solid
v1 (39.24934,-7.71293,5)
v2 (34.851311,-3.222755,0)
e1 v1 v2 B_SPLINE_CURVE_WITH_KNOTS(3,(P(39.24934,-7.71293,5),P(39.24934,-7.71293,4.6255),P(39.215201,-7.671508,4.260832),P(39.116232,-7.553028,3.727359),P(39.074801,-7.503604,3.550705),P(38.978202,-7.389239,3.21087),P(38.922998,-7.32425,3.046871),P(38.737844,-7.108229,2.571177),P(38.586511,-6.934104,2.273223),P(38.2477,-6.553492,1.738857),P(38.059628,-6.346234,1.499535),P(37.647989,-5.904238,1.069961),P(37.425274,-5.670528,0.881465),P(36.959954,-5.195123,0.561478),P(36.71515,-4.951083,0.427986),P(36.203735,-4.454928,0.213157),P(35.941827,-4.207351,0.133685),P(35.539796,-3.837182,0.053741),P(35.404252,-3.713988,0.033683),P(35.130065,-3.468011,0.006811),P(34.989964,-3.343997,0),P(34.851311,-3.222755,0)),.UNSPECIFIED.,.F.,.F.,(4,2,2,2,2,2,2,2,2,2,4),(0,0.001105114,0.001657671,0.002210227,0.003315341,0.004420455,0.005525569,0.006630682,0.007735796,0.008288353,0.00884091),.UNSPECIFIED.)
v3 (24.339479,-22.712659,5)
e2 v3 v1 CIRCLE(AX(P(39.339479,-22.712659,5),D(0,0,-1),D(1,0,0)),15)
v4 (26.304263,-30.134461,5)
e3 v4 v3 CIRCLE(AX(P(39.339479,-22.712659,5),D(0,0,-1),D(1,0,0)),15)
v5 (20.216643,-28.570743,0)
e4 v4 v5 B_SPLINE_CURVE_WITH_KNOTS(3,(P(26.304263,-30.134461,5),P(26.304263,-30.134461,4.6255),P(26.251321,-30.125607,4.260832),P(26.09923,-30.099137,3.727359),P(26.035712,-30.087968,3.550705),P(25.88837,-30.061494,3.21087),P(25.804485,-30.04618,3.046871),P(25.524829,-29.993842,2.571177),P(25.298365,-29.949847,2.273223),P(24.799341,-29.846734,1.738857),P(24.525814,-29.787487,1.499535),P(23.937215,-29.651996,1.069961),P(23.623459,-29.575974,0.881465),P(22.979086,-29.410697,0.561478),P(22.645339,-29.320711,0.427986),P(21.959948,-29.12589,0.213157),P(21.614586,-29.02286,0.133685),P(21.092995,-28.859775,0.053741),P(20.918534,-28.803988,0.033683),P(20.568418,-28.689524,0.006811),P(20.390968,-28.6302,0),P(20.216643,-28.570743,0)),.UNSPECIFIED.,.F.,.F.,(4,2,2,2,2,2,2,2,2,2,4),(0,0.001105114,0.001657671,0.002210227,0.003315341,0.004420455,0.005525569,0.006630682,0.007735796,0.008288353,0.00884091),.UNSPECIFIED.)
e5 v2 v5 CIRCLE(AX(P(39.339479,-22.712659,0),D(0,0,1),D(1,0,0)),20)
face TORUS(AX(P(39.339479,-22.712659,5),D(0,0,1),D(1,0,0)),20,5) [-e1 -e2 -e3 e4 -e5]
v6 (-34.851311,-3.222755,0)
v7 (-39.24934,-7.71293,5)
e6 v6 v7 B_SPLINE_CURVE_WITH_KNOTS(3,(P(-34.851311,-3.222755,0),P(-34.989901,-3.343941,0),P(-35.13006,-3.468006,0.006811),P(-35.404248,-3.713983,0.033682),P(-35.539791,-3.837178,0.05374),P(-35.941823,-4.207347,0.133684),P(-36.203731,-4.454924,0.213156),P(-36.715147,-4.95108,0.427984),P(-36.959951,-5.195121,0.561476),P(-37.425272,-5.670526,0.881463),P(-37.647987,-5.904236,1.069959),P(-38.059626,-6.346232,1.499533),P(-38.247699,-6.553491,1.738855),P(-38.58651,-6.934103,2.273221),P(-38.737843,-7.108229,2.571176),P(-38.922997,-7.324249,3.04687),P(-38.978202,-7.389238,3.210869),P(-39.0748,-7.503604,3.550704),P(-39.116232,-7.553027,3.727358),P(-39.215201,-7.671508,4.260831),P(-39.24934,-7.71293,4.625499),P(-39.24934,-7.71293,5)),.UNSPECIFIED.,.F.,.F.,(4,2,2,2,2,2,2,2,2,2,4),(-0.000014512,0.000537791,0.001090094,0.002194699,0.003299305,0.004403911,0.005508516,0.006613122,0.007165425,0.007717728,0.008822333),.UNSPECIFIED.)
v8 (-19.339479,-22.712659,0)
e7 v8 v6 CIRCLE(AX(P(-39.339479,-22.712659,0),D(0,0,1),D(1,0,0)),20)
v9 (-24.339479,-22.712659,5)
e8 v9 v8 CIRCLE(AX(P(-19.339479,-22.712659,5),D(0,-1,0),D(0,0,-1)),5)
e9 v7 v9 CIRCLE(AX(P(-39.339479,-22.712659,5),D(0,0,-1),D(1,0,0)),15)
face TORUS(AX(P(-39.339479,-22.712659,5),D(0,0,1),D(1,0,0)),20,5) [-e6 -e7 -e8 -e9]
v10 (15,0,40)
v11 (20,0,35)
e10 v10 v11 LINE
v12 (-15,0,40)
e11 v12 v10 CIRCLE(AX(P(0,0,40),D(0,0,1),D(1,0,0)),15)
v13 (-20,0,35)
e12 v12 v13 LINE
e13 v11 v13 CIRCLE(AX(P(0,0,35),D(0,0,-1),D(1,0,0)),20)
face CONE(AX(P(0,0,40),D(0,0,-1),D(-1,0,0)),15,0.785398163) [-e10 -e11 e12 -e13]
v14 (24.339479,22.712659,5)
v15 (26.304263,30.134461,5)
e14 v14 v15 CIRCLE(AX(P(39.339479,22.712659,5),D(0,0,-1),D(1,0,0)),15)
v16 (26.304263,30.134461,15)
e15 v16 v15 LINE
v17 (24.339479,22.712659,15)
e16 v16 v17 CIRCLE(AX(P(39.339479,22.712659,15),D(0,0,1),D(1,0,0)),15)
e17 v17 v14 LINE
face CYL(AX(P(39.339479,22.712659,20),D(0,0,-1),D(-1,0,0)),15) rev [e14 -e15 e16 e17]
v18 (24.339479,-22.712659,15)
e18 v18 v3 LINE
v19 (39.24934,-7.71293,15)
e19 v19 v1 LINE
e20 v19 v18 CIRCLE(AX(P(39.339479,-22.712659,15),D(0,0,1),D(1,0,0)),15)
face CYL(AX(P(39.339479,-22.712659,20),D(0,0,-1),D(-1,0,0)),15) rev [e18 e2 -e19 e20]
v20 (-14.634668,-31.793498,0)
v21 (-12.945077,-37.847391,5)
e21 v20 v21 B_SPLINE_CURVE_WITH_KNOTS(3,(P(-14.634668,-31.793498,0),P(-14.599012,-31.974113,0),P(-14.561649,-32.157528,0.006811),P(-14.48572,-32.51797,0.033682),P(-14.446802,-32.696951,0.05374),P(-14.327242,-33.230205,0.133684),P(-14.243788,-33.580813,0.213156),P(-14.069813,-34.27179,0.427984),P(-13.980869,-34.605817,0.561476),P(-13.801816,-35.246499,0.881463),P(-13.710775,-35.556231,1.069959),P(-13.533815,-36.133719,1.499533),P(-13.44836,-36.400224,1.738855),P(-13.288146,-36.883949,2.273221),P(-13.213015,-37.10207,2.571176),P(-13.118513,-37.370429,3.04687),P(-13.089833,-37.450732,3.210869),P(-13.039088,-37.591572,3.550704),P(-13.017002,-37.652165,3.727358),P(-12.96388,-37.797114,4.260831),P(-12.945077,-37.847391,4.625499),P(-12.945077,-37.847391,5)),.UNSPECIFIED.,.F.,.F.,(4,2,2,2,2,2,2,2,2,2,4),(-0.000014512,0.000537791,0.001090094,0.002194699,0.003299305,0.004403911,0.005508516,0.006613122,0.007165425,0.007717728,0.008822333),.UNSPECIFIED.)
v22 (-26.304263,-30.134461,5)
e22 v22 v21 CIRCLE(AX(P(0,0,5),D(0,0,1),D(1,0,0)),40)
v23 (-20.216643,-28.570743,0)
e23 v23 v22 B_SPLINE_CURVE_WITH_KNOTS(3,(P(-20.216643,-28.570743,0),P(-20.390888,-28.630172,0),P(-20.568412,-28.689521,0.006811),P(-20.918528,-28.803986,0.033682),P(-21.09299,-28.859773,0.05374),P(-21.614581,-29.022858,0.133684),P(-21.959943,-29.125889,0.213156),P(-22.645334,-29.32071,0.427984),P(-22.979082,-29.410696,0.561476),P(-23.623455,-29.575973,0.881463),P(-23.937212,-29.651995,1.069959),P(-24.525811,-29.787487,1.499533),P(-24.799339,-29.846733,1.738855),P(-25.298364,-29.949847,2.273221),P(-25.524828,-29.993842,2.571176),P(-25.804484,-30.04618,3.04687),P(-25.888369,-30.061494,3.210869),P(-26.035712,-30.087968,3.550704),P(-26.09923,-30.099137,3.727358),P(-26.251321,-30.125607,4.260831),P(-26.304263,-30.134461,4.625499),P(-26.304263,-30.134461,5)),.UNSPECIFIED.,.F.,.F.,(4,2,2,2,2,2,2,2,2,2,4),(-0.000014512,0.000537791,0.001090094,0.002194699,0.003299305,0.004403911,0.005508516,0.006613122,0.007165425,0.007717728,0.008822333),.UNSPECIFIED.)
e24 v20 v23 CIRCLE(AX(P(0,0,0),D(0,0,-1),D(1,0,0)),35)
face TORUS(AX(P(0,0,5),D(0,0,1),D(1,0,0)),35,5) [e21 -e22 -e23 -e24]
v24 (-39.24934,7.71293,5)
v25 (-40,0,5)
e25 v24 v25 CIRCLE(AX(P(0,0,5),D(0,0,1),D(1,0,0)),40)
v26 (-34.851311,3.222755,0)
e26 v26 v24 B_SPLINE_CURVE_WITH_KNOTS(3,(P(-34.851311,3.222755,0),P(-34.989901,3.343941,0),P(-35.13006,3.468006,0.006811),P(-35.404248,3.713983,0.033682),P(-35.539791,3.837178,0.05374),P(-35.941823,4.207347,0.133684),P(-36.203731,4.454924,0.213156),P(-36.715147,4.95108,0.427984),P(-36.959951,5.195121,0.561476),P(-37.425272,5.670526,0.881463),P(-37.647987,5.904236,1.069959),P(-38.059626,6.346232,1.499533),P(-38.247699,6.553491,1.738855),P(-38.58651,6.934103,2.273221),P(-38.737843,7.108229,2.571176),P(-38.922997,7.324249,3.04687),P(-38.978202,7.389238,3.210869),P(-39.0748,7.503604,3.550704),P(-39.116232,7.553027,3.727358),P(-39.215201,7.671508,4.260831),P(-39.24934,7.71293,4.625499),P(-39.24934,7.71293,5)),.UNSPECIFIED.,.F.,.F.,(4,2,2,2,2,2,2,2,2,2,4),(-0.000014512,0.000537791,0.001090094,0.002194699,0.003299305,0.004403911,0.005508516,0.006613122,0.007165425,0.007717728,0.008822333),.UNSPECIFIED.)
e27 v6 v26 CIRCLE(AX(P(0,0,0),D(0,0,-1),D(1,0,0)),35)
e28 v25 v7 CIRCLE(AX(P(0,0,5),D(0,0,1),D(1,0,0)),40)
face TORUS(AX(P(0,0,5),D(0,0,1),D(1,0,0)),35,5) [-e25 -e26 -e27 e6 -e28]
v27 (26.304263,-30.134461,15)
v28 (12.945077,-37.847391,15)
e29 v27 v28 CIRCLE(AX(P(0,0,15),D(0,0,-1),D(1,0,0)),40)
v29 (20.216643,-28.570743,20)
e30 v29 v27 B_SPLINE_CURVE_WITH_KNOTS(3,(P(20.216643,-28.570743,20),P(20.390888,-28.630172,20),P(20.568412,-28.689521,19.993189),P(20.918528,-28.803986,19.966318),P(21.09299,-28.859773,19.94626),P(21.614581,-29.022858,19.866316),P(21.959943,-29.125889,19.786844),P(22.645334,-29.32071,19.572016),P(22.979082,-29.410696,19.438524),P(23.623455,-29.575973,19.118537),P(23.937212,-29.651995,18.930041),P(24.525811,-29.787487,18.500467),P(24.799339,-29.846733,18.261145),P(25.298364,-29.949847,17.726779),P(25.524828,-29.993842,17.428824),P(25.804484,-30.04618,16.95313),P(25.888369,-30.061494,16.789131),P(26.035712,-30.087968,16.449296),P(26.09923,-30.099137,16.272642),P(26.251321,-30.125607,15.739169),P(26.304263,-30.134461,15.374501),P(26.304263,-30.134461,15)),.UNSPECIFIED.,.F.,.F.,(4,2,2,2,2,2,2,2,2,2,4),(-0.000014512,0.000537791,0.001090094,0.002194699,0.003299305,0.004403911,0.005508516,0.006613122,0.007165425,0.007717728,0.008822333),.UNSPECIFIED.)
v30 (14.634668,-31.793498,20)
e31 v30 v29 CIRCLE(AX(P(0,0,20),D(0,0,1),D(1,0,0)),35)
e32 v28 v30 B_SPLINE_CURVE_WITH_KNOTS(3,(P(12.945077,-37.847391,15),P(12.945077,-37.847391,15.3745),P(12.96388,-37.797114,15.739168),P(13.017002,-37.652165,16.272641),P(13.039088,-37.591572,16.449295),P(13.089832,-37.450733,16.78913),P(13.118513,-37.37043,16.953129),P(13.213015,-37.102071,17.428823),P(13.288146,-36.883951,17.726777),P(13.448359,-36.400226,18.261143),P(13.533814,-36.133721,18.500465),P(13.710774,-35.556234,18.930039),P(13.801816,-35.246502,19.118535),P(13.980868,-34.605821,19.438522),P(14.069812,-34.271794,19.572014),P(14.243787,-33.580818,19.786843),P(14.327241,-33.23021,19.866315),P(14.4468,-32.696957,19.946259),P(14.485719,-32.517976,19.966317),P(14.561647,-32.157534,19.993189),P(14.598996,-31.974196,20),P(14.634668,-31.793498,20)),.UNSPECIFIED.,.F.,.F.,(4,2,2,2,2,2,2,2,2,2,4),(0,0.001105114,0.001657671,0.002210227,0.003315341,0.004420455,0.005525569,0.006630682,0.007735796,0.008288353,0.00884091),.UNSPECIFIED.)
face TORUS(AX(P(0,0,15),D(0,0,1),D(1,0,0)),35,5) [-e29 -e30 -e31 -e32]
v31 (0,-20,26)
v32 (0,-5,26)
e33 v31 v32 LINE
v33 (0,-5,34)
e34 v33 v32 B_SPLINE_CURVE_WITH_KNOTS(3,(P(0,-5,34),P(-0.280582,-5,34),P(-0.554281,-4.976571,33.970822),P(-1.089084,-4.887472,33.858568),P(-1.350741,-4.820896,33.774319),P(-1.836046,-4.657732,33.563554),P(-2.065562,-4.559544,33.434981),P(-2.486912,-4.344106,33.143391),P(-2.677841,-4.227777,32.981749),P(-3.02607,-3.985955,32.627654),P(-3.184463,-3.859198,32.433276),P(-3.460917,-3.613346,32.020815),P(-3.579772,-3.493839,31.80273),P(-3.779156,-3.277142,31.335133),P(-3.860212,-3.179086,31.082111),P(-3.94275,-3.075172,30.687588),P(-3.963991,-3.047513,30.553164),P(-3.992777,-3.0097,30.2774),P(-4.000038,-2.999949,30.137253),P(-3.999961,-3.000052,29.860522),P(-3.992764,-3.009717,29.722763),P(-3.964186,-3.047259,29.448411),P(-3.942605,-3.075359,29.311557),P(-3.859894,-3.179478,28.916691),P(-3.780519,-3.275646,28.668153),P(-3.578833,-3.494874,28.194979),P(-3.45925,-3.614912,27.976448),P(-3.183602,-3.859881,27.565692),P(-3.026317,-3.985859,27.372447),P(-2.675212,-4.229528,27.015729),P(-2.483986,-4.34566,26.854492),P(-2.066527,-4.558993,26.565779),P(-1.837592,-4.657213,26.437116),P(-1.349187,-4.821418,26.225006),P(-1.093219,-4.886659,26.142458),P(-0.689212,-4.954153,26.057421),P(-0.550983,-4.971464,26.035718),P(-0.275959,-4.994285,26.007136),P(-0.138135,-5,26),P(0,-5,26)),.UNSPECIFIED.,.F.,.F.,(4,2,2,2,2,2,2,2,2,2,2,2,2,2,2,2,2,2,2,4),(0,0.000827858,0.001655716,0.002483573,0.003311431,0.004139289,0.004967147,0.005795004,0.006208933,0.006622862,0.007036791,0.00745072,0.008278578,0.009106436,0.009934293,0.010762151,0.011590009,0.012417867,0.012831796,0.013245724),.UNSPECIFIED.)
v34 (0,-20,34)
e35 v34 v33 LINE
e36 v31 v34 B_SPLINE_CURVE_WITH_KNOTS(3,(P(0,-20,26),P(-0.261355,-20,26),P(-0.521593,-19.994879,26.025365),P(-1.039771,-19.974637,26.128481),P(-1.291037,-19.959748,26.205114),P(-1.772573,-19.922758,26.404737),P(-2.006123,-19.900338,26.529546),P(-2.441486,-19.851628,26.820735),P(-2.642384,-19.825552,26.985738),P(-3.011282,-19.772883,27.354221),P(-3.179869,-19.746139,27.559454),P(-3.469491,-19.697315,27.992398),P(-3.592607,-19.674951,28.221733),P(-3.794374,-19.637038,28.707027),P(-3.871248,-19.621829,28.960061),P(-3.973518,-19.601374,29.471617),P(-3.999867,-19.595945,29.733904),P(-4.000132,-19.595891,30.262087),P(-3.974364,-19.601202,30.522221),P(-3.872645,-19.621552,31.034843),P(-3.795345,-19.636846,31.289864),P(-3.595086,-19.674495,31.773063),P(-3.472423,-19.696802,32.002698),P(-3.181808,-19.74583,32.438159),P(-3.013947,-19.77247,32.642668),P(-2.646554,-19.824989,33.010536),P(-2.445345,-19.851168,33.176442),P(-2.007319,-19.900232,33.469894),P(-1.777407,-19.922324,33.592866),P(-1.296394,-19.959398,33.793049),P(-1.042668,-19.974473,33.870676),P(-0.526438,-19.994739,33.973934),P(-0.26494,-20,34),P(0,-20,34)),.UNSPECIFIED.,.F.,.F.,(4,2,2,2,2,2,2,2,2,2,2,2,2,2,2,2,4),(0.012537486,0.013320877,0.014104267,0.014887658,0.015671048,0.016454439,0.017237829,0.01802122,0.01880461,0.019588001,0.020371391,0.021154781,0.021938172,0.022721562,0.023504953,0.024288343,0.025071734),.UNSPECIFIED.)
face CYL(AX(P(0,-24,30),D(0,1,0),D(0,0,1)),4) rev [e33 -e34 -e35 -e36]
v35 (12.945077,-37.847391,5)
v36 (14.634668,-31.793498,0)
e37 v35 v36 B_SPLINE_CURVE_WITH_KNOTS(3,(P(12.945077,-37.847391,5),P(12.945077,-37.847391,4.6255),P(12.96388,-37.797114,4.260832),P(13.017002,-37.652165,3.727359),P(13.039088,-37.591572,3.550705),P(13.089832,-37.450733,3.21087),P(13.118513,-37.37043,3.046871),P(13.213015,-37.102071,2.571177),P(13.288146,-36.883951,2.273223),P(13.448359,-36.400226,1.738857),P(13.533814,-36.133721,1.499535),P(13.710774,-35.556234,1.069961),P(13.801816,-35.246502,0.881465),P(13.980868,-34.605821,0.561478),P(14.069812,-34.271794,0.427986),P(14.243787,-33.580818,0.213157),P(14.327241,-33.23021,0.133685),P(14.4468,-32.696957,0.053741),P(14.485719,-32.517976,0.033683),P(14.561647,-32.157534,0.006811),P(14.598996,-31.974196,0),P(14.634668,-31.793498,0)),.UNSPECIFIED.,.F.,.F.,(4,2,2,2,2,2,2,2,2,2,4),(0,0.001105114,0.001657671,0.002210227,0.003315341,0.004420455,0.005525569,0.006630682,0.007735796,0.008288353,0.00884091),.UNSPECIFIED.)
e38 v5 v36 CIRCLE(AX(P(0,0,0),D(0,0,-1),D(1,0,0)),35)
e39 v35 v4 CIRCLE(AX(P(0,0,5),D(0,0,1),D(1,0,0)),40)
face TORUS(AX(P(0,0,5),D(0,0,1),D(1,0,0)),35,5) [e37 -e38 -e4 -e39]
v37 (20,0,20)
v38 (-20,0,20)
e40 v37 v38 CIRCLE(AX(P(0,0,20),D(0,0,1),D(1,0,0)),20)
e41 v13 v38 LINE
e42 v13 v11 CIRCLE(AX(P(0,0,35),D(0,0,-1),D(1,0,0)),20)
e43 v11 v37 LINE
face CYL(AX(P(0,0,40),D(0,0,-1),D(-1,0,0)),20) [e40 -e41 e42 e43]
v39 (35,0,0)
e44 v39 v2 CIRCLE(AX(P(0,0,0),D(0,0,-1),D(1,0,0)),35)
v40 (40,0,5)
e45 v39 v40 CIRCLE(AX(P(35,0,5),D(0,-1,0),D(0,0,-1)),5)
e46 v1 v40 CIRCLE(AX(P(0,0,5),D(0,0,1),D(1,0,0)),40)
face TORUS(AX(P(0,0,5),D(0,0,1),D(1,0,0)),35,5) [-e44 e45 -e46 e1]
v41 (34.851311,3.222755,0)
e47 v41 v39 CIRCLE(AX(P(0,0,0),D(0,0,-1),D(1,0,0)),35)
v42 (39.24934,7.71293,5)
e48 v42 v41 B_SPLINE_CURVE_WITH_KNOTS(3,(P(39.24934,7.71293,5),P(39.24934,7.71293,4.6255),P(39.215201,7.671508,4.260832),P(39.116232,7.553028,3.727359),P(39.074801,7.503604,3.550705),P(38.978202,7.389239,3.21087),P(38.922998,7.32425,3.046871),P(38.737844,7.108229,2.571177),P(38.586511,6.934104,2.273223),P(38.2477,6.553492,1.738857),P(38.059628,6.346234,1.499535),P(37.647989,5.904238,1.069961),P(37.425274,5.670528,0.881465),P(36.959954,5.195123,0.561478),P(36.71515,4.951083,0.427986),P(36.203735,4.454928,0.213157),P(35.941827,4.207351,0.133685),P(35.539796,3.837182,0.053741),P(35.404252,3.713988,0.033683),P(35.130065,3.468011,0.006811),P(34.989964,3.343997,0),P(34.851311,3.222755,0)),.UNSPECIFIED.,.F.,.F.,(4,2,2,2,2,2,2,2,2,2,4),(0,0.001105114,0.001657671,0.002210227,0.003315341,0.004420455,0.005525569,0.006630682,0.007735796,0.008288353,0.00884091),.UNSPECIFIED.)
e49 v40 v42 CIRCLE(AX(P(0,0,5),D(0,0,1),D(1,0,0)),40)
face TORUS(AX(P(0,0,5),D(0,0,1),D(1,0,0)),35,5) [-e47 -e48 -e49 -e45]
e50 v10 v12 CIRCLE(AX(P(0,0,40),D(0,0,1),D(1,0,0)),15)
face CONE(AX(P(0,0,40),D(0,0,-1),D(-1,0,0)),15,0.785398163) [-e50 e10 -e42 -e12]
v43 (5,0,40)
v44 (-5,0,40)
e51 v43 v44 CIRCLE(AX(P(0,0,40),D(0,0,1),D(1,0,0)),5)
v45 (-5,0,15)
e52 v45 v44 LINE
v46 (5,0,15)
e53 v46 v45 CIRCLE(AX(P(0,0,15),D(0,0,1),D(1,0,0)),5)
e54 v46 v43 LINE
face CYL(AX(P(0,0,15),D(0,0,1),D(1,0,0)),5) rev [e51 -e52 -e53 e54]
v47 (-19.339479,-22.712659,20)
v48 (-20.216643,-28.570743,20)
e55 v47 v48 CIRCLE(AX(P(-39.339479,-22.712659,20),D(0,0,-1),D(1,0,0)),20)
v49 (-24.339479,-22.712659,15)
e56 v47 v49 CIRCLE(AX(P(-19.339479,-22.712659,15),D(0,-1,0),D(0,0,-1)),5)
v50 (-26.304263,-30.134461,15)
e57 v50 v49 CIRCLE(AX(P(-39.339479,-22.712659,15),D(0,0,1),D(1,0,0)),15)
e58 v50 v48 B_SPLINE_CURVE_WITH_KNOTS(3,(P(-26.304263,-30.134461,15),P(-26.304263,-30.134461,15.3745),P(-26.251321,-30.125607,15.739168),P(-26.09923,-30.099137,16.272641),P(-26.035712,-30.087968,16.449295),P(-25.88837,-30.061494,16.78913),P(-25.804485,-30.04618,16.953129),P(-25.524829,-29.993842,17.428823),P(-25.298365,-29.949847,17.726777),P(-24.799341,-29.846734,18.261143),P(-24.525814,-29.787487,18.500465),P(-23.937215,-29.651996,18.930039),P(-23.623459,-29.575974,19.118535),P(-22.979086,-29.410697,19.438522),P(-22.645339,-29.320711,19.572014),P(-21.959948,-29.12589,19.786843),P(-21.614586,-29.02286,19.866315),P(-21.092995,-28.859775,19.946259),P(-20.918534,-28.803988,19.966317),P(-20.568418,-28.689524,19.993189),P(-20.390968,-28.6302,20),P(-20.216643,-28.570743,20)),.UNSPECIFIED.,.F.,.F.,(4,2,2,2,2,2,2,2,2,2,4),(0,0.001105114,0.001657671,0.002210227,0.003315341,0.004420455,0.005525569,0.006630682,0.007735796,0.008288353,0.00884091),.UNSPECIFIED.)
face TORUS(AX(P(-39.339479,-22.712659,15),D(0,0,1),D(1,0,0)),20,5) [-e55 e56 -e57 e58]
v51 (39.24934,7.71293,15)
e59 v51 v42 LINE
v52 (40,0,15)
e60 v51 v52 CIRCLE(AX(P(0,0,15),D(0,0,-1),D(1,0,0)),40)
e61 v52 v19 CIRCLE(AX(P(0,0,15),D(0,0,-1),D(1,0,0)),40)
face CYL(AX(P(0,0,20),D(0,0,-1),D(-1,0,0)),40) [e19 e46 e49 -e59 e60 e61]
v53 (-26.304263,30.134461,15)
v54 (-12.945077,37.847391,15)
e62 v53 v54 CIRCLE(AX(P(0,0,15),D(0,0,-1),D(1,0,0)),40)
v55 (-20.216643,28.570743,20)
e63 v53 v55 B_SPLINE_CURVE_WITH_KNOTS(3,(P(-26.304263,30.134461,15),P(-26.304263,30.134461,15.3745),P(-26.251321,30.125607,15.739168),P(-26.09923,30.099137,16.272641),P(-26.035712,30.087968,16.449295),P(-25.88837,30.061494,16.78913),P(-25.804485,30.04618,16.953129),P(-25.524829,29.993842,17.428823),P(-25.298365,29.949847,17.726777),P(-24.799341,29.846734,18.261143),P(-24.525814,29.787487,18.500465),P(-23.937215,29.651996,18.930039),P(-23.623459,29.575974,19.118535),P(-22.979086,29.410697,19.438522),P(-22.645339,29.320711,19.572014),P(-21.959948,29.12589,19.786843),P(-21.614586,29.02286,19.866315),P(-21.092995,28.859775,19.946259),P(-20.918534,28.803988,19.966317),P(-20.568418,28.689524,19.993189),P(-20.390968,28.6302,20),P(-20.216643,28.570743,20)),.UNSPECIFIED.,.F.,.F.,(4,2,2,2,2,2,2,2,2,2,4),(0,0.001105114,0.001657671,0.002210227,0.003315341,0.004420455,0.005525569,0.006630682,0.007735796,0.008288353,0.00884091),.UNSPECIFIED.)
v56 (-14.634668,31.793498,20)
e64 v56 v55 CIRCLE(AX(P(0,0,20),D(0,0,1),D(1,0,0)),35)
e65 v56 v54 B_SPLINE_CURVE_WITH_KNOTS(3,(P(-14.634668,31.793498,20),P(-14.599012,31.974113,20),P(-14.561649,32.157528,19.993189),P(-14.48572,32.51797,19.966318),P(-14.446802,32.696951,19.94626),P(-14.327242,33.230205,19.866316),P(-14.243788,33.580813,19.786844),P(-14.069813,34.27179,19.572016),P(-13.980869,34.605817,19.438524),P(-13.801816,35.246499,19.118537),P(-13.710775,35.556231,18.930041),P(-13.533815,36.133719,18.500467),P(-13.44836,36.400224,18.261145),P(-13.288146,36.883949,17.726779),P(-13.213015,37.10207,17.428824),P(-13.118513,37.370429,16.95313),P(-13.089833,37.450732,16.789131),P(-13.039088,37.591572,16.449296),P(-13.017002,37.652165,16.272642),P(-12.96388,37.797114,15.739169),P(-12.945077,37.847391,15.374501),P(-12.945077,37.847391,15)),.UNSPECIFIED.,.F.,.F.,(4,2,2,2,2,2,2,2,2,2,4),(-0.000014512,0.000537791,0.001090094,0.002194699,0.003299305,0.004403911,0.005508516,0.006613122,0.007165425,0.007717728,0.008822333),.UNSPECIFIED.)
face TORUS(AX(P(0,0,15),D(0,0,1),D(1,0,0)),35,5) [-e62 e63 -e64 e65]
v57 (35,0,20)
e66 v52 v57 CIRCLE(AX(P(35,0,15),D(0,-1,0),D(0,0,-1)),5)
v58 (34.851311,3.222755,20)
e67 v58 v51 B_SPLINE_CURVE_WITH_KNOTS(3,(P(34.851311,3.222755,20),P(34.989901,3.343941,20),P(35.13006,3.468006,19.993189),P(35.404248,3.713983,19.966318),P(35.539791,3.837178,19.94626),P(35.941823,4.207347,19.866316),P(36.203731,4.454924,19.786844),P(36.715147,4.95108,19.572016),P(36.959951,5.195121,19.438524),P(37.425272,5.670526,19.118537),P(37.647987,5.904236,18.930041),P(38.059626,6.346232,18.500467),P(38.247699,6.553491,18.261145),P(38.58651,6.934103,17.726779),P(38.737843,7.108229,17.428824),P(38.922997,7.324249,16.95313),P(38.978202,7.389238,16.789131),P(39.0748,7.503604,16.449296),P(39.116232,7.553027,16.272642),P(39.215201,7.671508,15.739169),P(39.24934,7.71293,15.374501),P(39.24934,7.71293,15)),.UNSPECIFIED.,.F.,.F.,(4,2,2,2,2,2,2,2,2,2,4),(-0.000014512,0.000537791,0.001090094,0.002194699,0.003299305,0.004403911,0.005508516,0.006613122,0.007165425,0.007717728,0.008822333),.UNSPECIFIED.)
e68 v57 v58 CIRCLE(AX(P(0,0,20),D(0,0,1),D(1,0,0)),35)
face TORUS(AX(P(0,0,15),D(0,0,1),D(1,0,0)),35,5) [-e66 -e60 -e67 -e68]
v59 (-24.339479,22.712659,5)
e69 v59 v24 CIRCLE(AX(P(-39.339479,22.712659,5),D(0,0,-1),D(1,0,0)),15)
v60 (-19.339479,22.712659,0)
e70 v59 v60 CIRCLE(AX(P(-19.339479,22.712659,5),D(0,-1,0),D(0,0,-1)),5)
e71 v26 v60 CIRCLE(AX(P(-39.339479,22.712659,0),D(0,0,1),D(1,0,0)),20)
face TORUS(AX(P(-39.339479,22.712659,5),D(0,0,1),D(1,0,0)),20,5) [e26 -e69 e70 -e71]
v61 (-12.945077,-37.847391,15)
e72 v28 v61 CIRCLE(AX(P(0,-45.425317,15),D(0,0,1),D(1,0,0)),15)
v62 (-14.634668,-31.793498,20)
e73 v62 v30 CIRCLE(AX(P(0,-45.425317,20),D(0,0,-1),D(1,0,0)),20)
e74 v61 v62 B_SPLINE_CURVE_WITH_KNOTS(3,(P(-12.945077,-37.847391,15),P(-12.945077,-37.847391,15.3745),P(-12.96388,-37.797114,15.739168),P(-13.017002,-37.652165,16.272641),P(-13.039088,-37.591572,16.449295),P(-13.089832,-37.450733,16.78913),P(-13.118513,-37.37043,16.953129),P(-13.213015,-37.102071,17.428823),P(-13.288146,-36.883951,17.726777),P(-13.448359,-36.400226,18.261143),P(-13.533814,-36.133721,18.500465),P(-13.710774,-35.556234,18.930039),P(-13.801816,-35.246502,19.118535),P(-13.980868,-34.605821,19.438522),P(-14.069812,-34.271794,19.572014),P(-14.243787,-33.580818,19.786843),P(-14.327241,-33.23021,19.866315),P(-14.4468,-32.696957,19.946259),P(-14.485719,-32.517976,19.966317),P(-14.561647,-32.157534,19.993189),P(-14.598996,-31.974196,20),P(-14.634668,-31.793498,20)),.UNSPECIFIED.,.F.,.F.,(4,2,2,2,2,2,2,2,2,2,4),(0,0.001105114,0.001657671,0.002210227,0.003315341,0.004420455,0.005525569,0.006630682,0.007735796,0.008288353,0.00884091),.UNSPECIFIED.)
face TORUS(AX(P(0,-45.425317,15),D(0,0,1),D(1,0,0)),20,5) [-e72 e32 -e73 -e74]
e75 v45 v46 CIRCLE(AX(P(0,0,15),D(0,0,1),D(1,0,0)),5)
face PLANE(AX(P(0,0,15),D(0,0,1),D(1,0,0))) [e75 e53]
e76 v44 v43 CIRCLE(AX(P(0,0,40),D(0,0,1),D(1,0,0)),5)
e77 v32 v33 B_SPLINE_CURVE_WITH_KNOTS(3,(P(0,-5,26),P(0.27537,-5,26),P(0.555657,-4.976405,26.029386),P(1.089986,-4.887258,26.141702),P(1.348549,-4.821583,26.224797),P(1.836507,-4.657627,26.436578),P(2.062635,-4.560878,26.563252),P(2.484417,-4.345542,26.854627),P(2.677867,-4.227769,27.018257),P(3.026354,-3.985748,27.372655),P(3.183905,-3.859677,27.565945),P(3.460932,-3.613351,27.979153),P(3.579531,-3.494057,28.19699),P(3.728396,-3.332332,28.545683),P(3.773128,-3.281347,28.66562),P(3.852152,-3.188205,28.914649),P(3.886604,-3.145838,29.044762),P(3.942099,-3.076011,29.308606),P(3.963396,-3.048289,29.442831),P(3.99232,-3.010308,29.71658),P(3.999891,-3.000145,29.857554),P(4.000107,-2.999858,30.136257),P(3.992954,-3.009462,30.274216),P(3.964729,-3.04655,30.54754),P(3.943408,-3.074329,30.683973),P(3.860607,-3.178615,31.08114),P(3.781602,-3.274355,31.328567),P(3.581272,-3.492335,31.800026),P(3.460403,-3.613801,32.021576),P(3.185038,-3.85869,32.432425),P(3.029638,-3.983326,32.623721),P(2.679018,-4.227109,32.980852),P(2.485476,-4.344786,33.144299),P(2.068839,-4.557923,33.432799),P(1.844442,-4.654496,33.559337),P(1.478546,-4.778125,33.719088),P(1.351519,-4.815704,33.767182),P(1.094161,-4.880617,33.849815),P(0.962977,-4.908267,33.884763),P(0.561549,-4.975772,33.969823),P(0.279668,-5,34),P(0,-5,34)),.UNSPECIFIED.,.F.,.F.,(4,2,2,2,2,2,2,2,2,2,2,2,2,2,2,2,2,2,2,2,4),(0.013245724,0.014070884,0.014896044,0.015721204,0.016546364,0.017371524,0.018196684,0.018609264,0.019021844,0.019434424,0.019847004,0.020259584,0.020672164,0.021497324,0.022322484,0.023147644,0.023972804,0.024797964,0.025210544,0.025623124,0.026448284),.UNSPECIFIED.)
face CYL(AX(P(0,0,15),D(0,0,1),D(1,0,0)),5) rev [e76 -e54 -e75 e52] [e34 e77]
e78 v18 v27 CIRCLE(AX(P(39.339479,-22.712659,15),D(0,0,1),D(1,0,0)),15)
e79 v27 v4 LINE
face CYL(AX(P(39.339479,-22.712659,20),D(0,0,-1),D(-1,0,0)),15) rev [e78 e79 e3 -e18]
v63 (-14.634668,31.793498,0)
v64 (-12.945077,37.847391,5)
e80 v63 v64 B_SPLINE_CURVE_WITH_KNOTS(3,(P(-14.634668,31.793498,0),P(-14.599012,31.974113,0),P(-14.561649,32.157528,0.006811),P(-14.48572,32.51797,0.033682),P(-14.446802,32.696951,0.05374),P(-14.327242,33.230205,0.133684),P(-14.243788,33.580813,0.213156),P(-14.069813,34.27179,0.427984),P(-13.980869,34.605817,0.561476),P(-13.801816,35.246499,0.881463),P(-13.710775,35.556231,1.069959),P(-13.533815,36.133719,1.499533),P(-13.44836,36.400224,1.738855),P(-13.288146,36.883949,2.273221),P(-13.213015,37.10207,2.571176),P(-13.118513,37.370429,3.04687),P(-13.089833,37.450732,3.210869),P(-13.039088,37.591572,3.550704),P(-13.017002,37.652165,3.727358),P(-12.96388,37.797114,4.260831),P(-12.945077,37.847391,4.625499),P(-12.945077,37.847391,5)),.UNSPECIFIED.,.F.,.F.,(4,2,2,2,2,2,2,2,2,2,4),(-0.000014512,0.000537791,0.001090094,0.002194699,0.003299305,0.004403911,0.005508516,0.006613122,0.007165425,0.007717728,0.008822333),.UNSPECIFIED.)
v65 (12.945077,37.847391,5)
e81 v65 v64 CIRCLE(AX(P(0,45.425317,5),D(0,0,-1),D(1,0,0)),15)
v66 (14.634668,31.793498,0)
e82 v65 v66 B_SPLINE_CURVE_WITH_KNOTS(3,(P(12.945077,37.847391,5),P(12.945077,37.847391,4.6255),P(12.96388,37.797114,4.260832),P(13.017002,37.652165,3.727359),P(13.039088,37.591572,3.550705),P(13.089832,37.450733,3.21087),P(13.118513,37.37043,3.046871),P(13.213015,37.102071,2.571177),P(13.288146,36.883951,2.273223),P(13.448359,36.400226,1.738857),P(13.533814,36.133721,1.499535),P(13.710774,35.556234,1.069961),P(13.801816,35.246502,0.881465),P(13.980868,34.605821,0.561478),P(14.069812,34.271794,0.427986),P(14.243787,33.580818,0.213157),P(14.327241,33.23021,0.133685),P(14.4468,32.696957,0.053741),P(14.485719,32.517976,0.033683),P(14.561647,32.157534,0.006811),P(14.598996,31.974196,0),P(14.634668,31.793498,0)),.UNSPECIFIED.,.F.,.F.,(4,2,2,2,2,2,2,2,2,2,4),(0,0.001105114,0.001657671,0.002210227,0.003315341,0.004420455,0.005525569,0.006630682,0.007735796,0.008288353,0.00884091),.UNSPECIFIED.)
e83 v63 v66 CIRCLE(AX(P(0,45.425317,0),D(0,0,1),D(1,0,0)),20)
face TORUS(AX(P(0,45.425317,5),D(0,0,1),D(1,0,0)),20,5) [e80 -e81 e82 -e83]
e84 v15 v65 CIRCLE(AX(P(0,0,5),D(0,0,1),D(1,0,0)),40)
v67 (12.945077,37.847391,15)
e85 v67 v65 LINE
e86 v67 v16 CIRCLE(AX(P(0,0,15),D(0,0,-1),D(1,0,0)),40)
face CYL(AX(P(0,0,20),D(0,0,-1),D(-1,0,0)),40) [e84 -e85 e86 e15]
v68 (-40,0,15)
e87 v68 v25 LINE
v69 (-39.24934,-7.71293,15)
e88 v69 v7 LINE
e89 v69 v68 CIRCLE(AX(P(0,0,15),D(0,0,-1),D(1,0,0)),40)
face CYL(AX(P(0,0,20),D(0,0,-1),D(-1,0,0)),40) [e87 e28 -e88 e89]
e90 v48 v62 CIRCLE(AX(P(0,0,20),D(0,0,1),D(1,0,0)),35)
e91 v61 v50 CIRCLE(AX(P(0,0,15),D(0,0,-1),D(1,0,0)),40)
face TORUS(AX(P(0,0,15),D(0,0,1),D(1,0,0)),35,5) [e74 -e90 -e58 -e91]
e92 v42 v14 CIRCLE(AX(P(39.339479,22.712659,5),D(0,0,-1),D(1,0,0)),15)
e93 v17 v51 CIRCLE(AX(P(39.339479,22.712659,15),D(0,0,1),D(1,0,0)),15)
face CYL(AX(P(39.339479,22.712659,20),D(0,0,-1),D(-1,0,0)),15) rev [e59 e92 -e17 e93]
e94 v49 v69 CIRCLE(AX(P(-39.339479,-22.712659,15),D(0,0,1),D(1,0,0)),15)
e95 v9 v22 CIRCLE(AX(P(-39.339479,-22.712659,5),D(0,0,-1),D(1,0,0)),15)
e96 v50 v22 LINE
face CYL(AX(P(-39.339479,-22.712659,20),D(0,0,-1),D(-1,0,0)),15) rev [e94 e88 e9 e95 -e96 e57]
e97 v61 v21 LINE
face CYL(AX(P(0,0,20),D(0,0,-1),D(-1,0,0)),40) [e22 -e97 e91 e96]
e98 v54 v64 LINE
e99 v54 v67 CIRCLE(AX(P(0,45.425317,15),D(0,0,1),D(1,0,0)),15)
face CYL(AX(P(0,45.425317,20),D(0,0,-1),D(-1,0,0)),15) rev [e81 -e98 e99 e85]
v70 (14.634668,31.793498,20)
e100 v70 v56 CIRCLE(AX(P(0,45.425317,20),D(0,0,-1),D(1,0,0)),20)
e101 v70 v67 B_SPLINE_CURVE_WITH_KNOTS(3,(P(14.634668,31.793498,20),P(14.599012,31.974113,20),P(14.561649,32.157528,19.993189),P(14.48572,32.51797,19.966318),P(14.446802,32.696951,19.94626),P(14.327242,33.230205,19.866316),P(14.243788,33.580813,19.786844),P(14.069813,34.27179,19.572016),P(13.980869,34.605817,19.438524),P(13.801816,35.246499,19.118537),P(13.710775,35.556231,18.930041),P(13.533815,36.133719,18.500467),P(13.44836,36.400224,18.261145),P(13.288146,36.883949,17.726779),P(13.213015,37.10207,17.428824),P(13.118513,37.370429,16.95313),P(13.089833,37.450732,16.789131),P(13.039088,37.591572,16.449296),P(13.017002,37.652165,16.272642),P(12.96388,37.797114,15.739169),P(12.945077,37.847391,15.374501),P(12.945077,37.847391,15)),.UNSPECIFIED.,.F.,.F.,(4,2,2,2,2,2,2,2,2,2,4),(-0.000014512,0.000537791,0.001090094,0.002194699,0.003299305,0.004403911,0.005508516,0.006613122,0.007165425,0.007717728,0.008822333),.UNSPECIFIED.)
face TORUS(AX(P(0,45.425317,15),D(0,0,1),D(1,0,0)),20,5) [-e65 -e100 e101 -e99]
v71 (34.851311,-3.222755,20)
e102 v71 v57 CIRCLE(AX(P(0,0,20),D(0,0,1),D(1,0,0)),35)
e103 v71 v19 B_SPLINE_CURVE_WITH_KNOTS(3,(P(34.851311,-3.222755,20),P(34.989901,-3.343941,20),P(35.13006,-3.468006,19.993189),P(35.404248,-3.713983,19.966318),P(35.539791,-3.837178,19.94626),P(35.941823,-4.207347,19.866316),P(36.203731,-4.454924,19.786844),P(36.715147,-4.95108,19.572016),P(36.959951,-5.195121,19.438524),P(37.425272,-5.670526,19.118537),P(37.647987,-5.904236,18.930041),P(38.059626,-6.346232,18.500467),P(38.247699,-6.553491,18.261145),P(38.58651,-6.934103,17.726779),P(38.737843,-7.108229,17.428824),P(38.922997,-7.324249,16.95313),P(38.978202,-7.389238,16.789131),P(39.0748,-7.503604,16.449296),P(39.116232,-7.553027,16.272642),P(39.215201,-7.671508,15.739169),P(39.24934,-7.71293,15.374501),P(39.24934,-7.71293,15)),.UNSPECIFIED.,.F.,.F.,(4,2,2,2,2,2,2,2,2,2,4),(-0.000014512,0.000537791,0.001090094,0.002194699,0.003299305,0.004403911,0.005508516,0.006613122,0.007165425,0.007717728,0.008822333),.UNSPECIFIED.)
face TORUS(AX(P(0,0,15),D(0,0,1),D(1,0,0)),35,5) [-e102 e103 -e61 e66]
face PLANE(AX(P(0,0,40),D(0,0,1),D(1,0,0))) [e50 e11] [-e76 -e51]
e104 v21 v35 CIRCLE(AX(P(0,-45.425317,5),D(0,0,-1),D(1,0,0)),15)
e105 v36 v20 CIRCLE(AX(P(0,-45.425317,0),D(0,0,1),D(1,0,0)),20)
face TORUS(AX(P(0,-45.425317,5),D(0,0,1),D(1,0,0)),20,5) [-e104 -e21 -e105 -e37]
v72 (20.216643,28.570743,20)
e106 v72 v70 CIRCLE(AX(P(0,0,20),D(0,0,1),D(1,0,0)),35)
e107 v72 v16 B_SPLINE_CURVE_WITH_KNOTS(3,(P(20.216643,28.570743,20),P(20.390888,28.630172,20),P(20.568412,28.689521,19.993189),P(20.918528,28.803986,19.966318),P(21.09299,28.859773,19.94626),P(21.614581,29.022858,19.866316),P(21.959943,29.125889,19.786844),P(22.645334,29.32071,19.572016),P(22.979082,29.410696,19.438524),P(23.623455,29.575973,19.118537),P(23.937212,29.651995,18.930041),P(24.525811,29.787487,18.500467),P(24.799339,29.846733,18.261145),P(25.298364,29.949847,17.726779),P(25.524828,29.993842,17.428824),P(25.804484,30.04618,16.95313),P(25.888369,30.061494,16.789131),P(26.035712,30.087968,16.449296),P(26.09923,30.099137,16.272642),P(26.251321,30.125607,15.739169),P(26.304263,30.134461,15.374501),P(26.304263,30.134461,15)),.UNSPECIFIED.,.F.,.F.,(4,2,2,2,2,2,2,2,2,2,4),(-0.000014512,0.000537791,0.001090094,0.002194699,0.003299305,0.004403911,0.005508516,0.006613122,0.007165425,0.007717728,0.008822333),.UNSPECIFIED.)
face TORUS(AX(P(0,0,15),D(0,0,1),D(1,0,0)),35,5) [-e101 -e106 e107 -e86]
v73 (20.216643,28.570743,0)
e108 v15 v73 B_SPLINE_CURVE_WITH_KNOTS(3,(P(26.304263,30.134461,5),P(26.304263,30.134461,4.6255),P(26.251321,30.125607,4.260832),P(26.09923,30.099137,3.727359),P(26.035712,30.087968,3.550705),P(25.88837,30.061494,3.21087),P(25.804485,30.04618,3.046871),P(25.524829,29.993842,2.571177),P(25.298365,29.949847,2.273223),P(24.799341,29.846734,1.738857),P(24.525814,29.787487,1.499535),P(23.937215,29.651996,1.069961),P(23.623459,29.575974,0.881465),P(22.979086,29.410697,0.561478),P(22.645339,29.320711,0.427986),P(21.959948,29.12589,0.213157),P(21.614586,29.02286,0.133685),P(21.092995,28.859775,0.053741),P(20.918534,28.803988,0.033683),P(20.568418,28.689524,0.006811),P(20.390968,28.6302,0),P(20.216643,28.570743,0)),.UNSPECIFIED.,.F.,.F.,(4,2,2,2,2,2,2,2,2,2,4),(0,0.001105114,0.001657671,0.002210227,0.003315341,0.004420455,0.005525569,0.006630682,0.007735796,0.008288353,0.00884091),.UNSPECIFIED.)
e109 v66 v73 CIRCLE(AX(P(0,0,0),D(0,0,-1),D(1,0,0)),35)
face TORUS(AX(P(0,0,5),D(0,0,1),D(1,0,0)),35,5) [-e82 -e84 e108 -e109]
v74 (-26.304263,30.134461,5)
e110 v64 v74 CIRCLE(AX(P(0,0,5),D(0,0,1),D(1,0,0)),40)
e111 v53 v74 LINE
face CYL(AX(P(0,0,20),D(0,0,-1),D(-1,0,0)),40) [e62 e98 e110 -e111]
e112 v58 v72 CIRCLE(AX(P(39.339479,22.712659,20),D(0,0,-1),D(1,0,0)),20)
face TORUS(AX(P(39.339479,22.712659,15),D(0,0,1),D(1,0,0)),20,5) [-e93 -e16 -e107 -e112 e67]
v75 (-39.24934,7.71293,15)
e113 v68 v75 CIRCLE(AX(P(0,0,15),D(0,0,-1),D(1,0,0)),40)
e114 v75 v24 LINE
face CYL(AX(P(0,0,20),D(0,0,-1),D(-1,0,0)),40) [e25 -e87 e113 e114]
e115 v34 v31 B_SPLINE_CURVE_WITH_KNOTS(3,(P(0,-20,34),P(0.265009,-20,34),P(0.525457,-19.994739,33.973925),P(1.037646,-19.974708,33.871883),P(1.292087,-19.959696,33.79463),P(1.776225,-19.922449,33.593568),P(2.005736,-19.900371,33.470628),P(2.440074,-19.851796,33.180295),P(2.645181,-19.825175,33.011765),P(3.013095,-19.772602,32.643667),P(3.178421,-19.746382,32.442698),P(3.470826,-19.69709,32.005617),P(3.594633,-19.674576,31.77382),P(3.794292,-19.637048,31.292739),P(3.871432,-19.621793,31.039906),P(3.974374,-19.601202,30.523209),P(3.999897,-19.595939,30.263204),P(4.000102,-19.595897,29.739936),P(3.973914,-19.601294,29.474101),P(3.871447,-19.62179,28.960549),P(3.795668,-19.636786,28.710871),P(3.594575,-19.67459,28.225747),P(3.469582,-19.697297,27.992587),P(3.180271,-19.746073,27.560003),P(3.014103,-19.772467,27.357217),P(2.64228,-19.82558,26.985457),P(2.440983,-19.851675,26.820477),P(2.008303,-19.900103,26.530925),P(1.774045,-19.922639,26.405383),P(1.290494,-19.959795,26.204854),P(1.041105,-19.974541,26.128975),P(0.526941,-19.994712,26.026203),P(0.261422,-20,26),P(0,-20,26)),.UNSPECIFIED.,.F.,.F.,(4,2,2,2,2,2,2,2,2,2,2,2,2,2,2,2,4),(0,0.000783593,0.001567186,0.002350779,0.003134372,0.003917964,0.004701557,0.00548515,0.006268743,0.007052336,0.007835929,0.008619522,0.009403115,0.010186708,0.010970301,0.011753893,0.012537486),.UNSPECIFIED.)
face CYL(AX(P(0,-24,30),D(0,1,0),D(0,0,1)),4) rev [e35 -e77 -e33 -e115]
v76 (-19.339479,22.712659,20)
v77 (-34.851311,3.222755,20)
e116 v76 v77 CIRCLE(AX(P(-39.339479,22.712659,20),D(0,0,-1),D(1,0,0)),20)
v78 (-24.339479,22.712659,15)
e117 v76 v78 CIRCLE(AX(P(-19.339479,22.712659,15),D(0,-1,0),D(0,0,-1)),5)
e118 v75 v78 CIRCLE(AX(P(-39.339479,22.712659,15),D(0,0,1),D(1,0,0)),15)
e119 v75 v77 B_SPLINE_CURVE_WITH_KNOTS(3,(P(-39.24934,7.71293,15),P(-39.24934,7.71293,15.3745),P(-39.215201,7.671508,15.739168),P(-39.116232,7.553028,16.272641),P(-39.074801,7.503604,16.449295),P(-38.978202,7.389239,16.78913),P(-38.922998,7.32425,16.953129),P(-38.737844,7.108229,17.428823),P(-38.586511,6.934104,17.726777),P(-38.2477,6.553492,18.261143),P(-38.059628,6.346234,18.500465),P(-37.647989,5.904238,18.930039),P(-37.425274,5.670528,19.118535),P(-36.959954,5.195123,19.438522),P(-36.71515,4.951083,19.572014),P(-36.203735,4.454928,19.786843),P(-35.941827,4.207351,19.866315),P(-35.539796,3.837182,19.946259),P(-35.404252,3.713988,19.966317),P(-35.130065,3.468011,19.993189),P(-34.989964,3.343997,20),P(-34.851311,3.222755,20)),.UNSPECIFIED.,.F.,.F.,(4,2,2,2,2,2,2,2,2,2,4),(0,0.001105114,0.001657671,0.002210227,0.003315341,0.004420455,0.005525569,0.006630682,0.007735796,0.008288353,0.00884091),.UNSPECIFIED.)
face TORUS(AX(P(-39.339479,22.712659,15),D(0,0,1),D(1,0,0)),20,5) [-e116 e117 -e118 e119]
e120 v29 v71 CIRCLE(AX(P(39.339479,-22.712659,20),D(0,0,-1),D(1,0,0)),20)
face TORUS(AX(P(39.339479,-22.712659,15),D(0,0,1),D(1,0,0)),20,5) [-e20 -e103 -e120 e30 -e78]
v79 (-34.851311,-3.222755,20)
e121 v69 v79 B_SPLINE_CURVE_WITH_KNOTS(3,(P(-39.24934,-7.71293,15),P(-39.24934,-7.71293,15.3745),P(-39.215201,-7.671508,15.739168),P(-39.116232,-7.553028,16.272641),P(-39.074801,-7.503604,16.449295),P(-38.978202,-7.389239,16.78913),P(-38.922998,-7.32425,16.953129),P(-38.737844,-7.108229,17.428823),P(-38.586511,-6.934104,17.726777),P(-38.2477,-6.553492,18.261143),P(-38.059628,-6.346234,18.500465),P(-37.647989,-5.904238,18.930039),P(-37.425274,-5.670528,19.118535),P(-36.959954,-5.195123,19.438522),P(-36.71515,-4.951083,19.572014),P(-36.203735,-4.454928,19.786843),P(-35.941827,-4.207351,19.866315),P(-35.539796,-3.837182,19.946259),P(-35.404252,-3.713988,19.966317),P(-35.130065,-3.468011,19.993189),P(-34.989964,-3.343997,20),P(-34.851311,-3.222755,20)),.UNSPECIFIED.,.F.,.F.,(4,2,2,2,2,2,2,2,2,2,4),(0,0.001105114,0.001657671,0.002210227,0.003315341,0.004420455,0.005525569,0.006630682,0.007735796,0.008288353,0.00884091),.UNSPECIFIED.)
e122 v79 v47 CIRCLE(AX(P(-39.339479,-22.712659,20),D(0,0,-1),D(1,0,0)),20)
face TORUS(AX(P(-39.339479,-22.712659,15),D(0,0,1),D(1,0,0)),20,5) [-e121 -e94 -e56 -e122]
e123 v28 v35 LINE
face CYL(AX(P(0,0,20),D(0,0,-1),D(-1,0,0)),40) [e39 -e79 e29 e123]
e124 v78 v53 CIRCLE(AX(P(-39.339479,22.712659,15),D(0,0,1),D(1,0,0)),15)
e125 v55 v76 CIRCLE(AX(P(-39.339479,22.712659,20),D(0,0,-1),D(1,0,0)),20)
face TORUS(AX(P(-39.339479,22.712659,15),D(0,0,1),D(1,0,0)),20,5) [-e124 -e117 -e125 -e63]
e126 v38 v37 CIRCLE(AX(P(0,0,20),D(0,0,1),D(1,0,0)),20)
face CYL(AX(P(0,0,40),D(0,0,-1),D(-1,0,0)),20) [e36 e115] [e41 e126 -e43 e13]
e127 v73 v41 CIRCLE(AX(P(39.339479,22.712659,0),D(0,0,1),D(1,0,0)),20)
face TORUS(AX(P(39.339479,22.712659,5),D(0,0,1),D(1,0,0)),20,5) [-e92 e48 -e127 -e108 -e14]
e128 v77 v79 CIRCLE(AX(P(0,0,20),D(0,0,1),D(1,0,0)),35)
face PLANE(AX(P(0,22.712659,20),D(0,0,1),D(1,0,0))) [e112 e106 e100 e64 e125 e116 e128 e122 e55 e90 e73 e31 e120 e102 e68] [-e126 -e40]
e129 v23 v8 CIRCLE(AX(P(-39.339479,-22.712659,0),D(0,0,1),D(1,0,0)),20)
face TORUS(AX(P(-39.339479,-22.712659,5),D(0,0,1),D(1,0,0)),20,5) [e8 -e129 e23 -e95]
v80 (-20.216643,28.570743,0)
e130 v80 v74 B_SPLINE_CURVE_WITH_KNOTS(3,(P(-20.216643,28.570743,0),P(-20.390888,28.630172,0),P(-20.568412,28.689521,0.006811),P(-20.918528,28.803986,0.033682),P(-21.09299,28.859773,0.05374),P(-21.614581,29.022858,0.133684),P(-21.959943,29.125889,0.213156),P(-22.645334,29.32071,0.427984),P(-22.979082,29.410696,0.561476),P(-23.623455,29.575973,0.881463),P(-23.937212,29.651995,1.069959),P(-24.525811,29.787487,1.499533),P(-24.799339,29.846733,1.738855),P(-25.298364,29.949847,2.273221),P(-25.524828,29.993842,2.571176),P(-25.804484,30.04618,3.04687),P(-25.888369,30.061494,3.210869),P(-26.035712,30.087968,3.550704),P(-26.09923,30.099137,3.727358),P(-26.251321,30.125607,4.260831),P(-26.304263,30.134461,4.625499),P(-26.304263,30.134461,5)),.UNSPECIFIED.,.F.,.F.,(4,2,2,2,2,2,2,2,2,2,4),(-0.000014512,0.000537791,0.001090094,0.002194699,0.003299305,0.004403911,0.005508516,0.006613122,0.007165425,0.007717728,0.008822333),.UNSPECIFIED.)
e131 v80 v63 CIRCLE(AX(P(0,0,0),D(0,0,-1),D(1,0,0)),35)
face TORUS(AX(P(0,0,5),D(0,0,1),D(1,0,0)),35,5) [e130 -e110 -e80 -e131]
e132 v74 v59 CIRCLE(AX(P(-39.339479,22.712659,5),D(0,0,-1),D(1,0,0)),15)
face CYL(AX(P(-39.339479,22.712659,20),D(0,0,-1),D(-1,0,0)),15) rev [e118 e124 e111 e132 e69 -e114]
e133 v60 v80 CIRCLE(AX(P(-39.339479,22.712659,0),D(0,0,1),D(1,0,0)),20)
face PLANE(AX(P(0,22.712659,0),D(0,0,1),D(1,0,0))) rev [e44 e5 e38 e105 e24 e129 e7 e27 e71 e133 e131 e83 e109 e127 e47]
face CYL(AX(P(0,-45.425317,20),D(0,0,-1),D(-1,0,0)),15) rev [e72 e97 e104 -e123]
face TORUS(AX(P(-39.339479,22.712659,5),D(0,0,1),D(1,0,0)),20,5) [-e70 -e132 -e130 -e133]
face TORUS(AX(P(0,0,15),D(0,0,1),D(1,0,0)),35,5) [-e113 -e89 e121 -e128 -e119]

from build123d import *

# Parameters (mm, degrees)
STAR_GRIP_BODY_DEPTH    = 20
HUB_SKETCH_R            = 20
HUB_SKETCH_R_2          = 17.5
HUB_BOSS_40_DEPTH       = 20
BORE_SKETCH_R           = 5
AXIAL_BORE_10_DEPTH     = 25
SET_SCREW_HOLE_SKETCH_R = 4
SET_SCREW_HOLE_8_DEPTH  = 24
HUB_CHAMFER_5X45_SIZE   = 5
GRIP_EDGE_FILLET_R5_A_R = 5
GRIP_EDGE_FILLET_R5_B_R = 5


with BuildPart() as part:
    # Star Grip Profile Sketch → Star Grip Body (new body)
    with BuildSketch(Plane.XY):
        with BuildLine():
            ThreePointArc((-39.249340356, 7.71292951), (-40, 0), (-39.249340356, -7.71292951))
            ThreePointArc((-39.249340356, -7.71292951), (-26.349097745, -15.212658676), (-26.304263071, -30.134461075))
            ThreePointArc((-26.304263071, -30.134461075), (-20, -34.641016151), (-12.945077285, -37.847390585))
            ThreePointArc((-12.945077285, -37.847390585), (0, -30.425317352), (12.945077285, -37.847390585))
            ThreePointArc((12.945077285, -37.847390585), (20, -34.641016151), (26.304263071, -30.134461075))
            ThreePointArc((26.304263071, -30.134461075), (26.349097745, -15.212658676), (39.249340356, -7.71292951))
            ThreePointArc((39.249340356, -7.71292951), (40, 0), (39.249340356, 7.71292951))
            ThreePointArc((39.249340356, 7.71292951), (26.349097745, 15.212658676), (26.304263071, 30.134461075))
            ThreePointArc((26.304263071, 30.134461075), (20, 34.641016151), (12.945077285, 37.847390585))
            ThreePointArc((12.945077285, 37.847390585), (0, 30.425317352), (-12.945077285, 37.847390585))
            ThreePointArc((-12.945077285, 37.847390585), (-20, 34.641016151), (-26.304263071, 30.134461075))
            ThreePointArc((-26.304263071, 30.134461075), (-26.349097745, 15.212658676), (-39.249340356, 7.71292951))
        make_face()
    extrude(amount=STAR_GRIP_BODY_DEPTH)

    # Hub Sketch → Hub Boss Ø40 (add)
    # profile 1 of 2: a face of its own
    with BuildSketch(Plane.XY.offset(20)):
        Circle(HUB_SKETCH_R)
        Circle(HUB_SKETCH_R_2, mode=Mode.SUBTRACT)
    # profile 2 of 2: a face of its own
    with BuildSketch(Plane.XY.offset(20)):
        Circle(HUB_SKETCH_R_2)
    extrude(amount=HUB_BOSS_40_DEPTH)

    # Bore Sketch → Axial Bore Ø10 (cut)
    with BuildSketch(Plane.XY.offset(40)):
        Circle(BORE_SKETCH_R)
    extrude(amount=-AXIAL_BORE_10_DEPTH, mode=Mode.SUBTRACT)

    # Set Screw Hole Sketch → Set Screw Hole Ø8 (cut)
    with BuildSketch(Plane(origin=(0, 0, 0), x_dir=(1, 0, 0), z_dir=(0, 1, 0))):
        with Locations(Location((0, -30, 0), (0, 0, 270))):
            Circle(SET_SCREW_HOLE_SKETCH_R)
    extrude(amount=-SET_SCREW_HOLE_8_DEPTH, mode=Mode.SUBTRACT)

    # Hub Chamfer 5x45
    hub_chamfer_5x45_edges = [part.edges().sort_by_distance(p)[0] for p in [
        (-20, 0, 40),
    ]]
    chamfer(hub_chamfer_5x45_edges, length=HUB_CHAMFER_5X45_SIZE)

    # Grip Edge Fillet R5 A
    grip_edge_fillet_r5_a_edges = [part.edges().sort_by_distance(p)[0] for p in [
        (-20, 34.641016151, 20),
        (-26.349097745, 15.212658676, 20),
        (-40, 0, 20),
        (-26.349097745, -15.212658676, 20),
        (-20, -34.641016151, 20),
        (0, -30.425317352, 20),
        (20, -34.641016151, 20),
        (26.349097745, -15.212658676, 20),
        (40, 0, 20),
        (26.349097745, 15.212658676, 20),
        (20, 34.641016151, 20),
        (0, 30.425317352, 20),
    ]]
    fillet(grip_edge_fillet_r5_a_edges, radius=GRIP_EDGE_FILLET_R5_A_R)

    # Grip Edge Fillet R5 B
    grip_edge_fillet_r5_b_edges = [part.edges().sort_by_distance(p)[0] for p in [
        (26.349097745, 15.212658676, 0),
        (40, 0, 0),
        (26.349097745, -15.212658676, 0),
        (20, -34.641016151, 0),
        (0, -30.425317352, 0),
        (-20, -34.641016151, 0),
        (-26.349097745, -15.212658676, 0),
        (-40, 0, 0),
        (-26.349097745, 15.212658676, 0),
        (-20, 34.641016151, 0),
        (0, 30.425317352, 0),
        (20, 34.641016151, 0),
    ]]
    fillet(grip_edge_fillet_r5_b_edges, radius=GRIP_EDGE_FILLET_R5_B_R)


solid = part.part
